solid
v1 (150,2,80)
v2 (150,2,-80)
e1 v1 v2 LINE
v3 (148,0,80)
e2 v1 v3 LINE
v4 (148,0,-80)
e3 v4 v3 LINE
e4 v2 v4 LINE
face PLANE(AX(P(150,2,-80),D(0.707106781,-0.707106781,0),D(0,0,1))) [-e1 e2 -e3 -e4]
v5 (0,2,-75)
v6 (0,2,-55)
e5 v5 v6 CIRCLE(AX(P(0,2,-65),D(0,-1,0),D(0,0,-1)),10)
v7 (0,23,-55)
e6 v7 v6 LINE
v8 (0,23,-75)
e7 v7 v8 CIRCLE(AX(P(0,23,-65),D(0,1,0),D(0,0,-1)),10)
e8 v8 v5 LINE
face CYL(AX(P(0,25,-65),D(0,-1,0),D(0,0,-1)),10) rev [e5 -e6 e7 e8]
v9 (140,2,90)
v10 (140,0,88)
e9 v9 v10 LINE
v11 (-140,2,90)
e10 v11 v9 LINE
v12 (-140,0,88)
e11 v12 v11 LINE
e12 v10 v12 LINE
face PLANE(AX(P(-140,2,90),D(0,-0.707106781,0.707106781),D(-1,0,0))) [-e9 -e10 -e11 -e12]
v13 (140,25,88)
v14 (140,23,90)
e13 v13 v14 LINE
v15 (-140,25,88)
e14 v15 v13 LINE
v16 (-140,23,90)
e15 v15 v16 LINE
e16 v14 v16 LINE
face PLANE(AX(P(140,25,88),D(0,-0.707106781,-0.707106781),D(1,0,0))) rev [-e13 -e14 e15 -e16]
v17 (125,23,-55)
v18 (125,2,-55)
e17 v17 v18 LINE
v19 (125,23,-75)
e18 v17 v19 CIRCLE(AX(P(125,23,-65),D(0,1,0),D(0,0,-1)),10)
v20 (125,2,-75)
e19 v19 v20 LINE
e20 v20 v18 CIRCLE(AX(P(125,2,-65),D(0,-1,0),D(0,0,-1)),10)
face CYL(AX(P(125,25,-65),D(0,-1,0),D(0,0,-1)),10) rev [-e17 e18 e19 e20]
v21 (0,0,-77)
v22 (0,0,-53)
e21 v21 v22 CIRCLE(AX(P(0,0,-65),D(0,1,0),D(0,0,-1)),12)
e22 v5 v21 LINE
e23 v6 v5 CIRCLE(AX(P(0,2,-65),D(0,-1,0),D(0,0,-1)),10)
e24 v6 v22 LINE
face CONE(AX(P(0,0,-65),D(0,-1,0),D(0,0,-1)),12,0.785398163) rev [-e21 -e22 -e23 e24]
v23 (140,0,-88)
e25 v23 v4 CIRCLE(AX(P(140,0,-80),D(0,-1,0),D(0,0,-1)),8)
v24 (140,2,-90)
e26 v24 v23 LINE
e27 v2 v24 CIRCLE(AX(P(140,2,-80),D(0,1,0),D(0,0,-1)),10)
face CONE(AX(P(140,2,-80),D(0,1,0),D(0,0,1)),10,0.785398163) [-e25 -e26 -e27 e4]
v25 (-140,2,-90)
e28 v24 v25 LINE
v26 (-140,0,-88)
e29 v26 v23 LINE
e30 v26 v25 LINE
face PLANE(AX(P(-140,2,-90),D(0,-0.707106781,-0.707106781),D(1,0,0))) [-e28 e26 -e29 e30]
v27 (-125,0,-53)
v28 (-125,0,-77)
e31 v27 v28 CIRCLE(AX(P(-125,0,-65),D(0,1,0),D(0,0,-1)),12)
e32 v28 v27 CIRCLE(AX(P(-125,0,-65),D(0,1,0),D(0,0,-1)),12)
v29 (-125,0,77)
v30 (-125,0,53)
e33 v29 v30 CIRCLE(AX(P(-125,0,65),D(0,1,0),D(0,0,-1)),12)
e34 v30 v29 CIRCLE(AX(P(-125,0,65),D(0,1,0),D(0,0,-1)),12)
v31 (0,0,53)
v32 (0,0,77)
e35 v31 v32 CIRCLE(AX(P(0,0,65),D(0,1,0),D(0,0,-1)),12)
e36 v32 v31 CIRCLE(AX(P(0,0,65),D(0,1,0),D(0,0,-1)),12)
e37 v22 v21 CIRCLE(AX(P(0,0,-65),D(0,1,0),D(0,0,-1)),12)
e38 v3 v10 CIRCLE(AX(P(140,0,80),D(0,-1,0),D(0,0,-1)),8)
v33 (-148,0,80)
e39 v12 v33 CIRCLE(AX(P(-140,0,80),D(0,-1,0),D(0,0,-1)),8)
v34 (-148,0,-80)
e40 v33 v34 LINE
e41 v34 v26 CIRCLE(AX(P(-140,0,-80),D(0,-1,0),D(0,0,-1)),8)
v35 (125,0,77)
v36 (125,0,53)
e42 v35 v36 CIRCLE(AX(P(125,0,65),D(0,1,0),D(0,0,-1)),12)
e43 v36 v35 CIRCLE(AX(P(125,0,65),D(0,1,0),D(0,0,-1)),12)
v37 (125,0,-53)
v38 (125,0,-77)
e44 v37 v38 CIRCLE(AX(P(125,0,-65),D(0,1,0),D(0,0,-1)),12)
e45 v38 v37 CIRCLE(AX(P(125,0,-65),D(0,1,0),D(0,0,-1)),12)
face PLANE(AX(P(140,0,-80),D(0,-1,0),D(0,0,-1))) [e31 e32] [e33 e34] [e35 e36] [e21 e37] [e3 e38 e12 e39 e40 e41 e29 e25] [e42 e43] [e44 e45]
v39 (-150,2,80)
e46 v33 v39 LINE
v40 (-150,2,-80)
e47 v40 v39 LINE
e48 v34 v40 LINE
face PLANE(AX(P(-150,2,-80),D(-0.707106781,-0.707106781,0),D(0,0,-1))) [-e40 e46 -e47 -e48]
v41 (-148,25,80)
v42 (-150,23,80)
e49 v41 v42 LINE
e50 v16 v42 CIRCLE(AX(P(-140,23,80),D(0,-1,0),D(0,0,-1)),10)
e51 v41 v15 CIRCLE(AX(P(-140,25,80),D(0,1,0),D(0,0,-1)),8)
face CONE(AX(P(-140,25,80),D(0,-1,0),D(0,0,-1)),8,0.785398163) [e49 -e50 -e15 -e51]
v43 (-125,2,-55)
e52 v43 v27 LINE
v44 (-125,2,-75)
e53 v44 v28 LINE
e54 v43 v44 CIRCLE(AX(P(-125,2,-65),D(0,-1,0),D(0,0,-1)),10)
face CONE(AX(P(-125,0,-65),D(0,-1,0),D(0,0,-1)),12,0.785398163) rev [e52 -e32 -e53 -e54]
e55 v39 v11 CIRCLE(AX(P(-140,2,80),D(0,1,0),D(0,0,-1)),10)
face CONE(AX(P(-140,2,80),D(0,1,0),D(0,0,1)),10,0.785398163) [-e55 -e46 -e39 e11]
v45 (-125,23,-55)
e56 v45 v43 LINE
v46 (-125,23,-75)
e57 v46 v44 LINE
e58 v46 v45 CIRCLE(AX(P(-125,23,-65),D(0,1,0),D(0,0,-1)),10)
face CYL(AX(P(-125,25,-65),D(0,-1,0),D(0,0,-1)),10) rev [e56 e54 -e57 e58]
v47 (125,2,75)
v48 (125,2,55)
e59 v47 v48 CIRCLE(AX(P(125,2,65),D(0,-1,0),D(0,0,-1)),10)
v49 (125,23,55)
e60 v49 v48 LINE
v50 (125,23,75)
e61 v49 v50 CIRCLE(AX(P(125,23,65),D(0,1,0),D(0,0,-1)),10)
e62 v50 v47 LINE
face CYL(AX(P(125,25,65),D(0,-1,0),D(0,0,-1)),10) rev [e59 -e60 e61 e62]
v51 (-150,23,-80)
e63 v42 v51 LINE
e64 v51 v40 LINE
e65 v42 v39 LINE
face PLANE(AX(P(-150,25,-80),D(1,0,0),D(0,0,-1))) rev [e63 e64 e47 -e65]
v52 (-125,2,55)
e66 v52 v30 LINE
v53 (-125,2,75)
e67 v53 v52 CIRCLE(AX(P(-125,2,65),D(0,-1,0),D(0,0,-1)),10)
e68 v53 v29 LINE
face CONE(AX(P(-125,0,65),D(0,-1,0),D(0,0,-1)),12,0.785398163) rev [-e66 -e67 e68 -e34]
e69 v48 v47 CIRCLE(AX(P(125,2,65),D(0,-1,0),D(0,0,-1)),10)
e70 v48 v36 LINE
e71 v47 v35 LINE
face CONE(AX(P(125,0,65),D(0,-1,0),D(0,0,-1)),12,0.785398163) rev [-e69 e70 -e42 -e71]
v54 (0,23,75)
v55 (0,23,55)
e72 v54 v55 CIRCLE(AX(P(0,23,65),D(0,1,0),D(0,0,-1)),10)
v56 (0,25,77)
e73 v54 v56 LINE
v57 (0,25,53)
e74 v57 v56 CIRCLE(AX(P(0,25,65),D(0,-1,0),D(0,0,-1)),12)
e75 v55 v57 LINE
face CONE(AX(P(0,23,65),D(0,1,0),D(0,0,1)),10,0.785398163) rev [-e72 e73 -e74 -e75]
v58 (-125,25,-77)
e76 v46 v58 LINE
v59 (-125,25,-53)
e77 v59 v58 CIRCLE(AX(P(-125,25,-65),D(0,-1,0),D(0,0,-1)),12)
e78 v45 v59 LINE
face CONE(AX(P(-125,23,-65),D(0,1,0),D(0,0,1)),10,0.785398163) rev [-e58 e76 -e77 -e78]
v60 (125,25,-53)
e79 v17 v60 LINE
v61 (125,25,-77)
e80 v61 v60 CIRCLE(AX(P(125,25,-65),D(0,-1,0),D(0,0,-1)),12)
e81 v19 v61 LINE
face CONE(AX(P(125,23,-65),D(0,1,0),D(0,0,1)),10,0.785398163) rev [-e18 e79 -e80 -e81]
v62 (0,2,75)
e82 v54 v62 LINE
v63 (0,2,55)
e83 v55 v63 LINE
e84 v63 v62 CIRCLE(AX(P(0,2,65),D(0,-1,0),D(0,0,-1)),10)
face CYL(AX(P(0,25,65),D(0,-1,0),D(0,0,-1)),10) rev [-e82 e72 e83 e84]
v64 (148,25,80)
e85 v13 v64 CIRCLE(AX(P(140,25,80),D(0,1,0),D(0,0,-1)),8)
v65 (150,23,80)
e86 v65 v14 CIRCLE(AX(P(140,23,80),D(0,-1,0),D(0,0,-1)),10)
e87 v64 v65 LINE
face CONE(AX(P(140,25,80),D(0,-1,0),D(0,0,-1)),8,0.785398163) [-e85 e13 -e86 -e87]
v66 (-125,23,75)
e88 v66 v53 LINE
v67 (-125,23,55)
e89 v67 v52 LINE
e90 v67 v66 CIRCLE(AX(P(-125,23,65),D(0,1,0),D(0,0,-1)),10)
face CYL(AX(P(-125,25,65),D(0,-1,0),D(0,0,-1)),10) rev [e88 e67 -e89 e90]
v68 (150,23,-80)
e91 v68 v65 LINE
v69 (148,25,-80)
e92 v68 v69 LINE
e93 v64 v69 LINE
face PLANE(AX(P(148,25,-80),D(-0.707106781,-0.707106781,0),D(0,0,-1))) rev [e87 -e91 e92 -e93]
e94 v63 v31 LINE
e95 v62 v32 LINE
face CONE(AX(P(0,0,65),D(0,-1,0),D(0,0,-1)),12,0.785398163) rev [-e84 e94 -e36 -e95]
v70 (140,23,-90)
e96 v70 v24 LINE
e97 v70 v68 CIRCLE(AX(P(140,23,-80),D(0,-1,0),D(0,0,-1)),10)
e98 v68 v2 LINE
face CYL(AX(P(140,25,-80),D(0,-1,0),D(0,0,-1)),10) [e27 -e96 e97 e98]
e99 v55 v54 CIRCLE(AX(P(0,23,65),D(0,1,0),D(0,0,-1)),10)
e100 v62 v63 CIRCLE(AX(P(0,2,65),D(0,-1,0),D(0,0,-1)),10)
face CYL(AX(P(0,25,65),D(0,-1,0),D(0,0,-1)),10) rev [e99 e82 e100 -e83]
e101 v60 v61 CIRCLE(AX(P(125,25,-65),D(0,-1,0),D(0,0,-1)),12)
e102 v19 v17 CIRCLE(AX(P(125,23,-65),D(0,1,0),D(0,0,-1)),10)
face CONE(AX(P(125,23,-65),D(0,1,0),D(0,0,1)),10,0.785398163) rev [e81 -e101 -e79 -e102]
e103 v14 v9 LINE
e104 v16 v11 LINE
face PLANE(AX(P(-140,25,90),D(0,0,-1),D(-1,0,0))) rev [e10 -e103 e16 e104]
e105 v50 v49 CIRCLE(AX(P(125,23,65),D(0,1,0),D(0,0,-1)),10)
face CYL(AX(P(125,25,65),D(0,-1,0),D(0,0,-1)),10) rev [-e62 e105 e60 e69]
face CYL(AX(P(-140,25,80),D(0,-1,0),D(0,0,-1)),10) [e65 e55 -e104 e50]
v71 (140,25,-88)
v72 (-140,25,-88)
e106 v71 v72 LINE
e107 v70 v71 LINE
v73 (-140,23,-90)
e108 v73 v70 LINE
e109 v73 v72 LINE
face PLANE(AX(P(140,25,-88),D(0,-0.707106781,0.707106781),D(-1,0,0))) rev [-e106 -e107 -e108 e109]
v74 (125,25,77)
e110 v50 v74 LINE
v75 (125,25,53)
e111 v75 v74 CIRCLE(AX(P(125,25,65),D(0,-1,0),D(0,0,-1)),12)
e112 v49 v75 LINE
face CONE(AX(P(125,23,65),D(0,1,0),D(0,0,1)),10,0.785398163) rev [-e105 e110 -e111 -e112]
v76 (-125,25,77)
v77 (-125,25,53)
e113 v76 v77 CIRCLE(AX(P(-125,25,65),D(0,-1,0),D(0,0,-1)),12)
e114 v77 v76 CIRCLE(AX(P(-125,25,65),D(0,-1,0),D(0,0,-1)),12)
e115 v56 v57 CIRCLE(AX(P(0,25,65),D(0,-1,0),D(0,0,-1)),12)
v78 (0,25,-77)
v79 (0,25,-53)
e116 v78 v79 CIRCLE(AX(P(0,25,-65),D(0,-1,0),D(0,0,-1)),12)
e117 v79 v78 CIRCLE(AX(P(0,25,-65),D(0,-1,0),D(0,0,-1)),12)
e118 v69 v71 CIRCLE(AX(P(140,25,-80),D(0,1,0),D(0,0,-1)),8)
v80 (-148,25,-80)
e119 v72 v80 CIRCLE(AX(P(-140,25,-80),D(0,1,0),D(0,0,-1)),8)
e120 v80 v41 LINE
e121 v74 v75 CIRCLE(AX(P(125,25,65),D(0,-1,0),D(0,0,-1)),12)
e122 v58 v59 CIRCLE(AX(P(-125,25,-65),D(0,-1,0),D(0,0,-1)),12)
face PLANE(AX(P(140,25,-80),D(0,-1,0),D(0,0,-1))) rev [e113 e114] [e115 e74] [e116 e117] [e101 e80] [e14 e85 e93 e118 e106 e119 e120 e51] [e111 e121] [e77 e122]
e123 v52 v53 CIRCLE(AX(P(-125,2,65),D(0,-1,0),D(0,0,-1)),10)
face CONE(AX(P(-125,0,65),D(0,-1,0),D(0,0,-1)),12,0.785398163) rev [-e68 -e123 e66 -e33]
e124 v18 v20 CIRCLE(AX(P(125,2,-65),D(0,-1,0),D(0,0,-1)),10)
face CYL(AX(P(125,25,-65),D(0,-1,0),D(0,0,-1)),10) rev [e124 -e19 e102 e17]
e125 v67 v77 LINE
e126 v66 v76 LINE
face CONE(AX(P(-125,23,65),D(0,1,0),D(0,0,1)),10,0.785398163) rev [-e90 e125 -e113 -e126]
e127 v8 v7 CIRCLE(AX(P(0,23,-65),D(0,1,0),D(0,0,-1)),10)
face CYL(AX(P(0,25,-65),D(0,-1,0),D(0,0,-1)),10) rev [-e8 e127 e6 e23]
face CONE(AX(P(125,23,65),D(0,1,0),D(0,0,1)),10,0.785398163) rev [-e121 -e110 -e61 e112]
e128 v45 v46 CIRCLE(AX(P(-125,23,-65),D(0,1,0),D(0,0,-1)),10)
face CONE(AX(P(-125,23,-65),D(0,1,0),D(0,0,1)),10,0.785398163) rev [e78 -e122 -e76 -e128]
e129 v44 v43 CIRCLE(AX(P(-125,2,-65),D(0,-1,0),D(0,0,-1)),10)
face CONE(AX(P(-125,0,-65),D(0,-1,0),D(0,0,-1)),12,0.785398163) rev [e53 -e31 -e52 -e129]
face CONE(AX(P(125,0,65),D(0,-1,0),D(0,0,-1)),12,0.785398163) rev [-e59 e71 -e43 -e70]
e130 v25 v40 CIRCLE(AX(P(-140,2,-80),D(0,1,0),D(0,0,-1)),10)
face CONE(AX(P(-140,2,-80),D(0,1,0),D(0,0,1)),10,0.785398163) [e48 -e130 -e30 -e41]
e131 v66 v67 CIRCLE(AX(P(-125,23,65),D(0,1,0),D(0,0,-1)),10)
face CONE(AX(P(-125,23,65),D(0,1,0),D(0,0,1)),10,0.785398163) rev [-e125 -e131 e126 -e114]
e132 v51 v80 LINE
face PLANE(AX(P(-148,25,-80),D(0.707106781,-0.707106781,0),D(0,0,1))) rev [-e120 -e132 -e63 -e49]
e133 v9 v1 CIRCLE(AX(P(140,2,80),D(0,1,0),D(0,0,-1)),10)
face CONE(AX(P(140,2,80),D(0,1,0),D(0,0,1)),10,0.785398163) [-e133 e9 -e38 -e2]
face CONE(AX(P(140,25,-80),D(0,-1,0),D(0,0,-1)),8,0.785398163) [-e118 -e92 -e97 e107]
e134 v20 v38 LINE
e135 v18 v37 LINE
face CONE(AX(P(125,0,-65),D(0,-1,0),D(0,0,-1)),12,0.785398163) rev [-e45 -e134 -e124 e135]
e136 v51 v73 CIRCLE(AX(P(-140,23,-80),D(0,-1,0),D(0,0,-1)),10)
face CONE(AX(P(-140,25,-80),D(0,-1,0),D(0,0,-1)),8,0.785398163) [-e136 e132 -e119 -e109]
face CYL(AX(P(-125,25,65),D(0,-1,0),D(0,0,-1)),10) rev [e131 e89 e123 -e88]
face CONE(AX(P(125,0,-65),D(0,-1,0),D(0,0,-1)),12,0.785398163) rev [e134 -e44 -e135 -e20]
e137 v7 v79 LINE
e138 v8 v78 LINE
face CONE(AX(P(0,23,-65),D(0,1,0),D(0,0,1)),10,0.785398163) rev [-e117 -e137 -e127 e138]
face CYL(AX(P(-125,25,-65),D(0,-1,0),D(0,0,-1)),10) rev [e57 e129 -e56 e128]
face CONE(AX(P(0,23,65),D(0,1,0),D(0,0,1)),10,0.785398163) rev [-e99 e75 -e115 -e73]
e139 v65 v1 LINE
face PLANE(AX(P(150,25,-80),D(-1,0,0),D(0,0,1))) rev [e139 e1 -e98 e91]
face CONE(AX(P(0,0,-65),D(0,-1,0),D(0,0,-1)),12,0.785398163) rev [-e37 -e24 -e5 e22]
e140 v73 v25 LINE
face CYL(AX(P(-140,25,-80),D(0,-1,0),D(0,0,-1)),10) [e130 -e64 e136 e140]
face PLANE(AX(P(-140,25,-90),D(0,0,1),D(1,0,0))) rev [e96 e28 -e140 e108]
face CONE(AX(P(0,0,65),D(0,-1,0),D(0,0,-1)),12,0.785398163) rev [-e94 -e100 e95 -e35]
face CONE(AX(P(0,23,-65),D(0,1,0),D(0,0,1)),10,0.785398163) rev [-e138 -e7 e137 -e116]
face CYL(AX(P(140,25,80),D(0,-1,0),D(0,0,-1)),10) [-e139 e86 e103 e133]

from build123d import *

# Parameters (mm, degrees)
PLATE_OUTLINE_AND_HOLE_SKETCH_R = 10
BASE_PLATE_25MM_DEPTH           = 25
EDGE_CHAMFER_2X45DEG_SIZE       = 2


with BuildPart() as part:
    # Plate Outline and Hole Sketch → Base Plate 25mm (new body)
    with BuildSketch(Plane(origin=(0, 0, 0), x_dir=(1, 0, 0), z_dir=(0, 1, 0))):
        with BuildLine():
            Line((-140, 90), (140, 90))
            ThreePointArc((140, 90), (147.071067812, 87.071067812), (150, 80))
            Line((150, 80), (150, -80))
            ThreePointArc((150, -80), (147.071067812, -87.071067812), (140, -90))
            Line((140, -90), (-140, -90))
            ThreePointArc((-140, -90), (-147.071067812, -87.071067812), (-150, -80))
            Line((-150, -80), (-150, 80))
            ThreePointArc((-150, 80), (-147.071067812, 87.071067812), (-140, 90))
        make_face()
        with Locations(Location((-125, 65, 0), (0, 0, 270))):
            Circle(PLATE_OUTLINE_AND_HOLE_SKETCH_R, mode=Mode.SUBTRACT)
        with Locations(Location((-125, -65, 0), (0, 0, 90))):
            Circle(PLATE_OUTLINE_AND_HOLE_SKETCH_R, mode=Mode.SUBTRACT)
        with Locations(Location((125, 65, 0), (0, 0, 90))):
            Circle(PLATE_OUTLINE_AND_HOLE_SKETCH_R, mode=Mode.SUBTRACT)
        with Locations(Location((125, -65, 0), (0, 0, 270))):
            Circle(PLATE_OUTLINE_AND_HOLE_SKETCH_R, mode=Mode.SUBTRACT)
        with Locations(Location((0, 65, 0), (0, 0, 270))):
            Circle(PLATE_OUTLINE_AND_HOLE_SKETCH_R, mode=Mode.SUBTRACT)
        with Locations(Location((0, -65, 0), (0, 0, 270))):
            Circle(PLATE_OUTLINE_AND_HOLE_SKETCH_R, mode=Mode.SUBTRACT)
    extrude(amount=BASE_PLATE_25MM_DEPTH)

    # Edge Chamfer 2x45deg
    edge_chamfer_2x45deg_edges = [part.edges().sort_by_distance(p)[0] for p in [
        (-150, 0, 0),
        (-147.071067812, 0, -87.071067812),
        (0, 0, -90),
        (147.071067812, 0, -87.071067812),
        (-147.071067812, 25, -87.071067812),
        (-150, 25, 0),
        (-147.071067812, 25, 87.071067812),
        (-125, 0, -75),
        (-125, 25, -75),
        (0, 25, 90),
        (-125, 0, 75),
        (-125, 25, 75),
        (147.071067812, 25, 87.071067812),
        (125, 0, -55),
        (125, 25, -55),
        (150, 25, 0),
        (125, 0, 55),
        (125, 25, 55),
        (0, 0, -75),
        (0, 25, -75),
        (0, 0, 55),
        (0, 25, 55),
        (147.071067812, 25, -87.071067812),
        (150, 0, 0),
        (0, 25, -90),
        (147.071067812, 0, 87.071067812),
        (0, 0, 90),
        (-147.071067812, 0, 87.071067812),
    ]]
    chamfer(edge_chamfer_2x45deg_edges, length=EDGE_CHAMFER_2X45DEG_SIZE)


solid = part.part
